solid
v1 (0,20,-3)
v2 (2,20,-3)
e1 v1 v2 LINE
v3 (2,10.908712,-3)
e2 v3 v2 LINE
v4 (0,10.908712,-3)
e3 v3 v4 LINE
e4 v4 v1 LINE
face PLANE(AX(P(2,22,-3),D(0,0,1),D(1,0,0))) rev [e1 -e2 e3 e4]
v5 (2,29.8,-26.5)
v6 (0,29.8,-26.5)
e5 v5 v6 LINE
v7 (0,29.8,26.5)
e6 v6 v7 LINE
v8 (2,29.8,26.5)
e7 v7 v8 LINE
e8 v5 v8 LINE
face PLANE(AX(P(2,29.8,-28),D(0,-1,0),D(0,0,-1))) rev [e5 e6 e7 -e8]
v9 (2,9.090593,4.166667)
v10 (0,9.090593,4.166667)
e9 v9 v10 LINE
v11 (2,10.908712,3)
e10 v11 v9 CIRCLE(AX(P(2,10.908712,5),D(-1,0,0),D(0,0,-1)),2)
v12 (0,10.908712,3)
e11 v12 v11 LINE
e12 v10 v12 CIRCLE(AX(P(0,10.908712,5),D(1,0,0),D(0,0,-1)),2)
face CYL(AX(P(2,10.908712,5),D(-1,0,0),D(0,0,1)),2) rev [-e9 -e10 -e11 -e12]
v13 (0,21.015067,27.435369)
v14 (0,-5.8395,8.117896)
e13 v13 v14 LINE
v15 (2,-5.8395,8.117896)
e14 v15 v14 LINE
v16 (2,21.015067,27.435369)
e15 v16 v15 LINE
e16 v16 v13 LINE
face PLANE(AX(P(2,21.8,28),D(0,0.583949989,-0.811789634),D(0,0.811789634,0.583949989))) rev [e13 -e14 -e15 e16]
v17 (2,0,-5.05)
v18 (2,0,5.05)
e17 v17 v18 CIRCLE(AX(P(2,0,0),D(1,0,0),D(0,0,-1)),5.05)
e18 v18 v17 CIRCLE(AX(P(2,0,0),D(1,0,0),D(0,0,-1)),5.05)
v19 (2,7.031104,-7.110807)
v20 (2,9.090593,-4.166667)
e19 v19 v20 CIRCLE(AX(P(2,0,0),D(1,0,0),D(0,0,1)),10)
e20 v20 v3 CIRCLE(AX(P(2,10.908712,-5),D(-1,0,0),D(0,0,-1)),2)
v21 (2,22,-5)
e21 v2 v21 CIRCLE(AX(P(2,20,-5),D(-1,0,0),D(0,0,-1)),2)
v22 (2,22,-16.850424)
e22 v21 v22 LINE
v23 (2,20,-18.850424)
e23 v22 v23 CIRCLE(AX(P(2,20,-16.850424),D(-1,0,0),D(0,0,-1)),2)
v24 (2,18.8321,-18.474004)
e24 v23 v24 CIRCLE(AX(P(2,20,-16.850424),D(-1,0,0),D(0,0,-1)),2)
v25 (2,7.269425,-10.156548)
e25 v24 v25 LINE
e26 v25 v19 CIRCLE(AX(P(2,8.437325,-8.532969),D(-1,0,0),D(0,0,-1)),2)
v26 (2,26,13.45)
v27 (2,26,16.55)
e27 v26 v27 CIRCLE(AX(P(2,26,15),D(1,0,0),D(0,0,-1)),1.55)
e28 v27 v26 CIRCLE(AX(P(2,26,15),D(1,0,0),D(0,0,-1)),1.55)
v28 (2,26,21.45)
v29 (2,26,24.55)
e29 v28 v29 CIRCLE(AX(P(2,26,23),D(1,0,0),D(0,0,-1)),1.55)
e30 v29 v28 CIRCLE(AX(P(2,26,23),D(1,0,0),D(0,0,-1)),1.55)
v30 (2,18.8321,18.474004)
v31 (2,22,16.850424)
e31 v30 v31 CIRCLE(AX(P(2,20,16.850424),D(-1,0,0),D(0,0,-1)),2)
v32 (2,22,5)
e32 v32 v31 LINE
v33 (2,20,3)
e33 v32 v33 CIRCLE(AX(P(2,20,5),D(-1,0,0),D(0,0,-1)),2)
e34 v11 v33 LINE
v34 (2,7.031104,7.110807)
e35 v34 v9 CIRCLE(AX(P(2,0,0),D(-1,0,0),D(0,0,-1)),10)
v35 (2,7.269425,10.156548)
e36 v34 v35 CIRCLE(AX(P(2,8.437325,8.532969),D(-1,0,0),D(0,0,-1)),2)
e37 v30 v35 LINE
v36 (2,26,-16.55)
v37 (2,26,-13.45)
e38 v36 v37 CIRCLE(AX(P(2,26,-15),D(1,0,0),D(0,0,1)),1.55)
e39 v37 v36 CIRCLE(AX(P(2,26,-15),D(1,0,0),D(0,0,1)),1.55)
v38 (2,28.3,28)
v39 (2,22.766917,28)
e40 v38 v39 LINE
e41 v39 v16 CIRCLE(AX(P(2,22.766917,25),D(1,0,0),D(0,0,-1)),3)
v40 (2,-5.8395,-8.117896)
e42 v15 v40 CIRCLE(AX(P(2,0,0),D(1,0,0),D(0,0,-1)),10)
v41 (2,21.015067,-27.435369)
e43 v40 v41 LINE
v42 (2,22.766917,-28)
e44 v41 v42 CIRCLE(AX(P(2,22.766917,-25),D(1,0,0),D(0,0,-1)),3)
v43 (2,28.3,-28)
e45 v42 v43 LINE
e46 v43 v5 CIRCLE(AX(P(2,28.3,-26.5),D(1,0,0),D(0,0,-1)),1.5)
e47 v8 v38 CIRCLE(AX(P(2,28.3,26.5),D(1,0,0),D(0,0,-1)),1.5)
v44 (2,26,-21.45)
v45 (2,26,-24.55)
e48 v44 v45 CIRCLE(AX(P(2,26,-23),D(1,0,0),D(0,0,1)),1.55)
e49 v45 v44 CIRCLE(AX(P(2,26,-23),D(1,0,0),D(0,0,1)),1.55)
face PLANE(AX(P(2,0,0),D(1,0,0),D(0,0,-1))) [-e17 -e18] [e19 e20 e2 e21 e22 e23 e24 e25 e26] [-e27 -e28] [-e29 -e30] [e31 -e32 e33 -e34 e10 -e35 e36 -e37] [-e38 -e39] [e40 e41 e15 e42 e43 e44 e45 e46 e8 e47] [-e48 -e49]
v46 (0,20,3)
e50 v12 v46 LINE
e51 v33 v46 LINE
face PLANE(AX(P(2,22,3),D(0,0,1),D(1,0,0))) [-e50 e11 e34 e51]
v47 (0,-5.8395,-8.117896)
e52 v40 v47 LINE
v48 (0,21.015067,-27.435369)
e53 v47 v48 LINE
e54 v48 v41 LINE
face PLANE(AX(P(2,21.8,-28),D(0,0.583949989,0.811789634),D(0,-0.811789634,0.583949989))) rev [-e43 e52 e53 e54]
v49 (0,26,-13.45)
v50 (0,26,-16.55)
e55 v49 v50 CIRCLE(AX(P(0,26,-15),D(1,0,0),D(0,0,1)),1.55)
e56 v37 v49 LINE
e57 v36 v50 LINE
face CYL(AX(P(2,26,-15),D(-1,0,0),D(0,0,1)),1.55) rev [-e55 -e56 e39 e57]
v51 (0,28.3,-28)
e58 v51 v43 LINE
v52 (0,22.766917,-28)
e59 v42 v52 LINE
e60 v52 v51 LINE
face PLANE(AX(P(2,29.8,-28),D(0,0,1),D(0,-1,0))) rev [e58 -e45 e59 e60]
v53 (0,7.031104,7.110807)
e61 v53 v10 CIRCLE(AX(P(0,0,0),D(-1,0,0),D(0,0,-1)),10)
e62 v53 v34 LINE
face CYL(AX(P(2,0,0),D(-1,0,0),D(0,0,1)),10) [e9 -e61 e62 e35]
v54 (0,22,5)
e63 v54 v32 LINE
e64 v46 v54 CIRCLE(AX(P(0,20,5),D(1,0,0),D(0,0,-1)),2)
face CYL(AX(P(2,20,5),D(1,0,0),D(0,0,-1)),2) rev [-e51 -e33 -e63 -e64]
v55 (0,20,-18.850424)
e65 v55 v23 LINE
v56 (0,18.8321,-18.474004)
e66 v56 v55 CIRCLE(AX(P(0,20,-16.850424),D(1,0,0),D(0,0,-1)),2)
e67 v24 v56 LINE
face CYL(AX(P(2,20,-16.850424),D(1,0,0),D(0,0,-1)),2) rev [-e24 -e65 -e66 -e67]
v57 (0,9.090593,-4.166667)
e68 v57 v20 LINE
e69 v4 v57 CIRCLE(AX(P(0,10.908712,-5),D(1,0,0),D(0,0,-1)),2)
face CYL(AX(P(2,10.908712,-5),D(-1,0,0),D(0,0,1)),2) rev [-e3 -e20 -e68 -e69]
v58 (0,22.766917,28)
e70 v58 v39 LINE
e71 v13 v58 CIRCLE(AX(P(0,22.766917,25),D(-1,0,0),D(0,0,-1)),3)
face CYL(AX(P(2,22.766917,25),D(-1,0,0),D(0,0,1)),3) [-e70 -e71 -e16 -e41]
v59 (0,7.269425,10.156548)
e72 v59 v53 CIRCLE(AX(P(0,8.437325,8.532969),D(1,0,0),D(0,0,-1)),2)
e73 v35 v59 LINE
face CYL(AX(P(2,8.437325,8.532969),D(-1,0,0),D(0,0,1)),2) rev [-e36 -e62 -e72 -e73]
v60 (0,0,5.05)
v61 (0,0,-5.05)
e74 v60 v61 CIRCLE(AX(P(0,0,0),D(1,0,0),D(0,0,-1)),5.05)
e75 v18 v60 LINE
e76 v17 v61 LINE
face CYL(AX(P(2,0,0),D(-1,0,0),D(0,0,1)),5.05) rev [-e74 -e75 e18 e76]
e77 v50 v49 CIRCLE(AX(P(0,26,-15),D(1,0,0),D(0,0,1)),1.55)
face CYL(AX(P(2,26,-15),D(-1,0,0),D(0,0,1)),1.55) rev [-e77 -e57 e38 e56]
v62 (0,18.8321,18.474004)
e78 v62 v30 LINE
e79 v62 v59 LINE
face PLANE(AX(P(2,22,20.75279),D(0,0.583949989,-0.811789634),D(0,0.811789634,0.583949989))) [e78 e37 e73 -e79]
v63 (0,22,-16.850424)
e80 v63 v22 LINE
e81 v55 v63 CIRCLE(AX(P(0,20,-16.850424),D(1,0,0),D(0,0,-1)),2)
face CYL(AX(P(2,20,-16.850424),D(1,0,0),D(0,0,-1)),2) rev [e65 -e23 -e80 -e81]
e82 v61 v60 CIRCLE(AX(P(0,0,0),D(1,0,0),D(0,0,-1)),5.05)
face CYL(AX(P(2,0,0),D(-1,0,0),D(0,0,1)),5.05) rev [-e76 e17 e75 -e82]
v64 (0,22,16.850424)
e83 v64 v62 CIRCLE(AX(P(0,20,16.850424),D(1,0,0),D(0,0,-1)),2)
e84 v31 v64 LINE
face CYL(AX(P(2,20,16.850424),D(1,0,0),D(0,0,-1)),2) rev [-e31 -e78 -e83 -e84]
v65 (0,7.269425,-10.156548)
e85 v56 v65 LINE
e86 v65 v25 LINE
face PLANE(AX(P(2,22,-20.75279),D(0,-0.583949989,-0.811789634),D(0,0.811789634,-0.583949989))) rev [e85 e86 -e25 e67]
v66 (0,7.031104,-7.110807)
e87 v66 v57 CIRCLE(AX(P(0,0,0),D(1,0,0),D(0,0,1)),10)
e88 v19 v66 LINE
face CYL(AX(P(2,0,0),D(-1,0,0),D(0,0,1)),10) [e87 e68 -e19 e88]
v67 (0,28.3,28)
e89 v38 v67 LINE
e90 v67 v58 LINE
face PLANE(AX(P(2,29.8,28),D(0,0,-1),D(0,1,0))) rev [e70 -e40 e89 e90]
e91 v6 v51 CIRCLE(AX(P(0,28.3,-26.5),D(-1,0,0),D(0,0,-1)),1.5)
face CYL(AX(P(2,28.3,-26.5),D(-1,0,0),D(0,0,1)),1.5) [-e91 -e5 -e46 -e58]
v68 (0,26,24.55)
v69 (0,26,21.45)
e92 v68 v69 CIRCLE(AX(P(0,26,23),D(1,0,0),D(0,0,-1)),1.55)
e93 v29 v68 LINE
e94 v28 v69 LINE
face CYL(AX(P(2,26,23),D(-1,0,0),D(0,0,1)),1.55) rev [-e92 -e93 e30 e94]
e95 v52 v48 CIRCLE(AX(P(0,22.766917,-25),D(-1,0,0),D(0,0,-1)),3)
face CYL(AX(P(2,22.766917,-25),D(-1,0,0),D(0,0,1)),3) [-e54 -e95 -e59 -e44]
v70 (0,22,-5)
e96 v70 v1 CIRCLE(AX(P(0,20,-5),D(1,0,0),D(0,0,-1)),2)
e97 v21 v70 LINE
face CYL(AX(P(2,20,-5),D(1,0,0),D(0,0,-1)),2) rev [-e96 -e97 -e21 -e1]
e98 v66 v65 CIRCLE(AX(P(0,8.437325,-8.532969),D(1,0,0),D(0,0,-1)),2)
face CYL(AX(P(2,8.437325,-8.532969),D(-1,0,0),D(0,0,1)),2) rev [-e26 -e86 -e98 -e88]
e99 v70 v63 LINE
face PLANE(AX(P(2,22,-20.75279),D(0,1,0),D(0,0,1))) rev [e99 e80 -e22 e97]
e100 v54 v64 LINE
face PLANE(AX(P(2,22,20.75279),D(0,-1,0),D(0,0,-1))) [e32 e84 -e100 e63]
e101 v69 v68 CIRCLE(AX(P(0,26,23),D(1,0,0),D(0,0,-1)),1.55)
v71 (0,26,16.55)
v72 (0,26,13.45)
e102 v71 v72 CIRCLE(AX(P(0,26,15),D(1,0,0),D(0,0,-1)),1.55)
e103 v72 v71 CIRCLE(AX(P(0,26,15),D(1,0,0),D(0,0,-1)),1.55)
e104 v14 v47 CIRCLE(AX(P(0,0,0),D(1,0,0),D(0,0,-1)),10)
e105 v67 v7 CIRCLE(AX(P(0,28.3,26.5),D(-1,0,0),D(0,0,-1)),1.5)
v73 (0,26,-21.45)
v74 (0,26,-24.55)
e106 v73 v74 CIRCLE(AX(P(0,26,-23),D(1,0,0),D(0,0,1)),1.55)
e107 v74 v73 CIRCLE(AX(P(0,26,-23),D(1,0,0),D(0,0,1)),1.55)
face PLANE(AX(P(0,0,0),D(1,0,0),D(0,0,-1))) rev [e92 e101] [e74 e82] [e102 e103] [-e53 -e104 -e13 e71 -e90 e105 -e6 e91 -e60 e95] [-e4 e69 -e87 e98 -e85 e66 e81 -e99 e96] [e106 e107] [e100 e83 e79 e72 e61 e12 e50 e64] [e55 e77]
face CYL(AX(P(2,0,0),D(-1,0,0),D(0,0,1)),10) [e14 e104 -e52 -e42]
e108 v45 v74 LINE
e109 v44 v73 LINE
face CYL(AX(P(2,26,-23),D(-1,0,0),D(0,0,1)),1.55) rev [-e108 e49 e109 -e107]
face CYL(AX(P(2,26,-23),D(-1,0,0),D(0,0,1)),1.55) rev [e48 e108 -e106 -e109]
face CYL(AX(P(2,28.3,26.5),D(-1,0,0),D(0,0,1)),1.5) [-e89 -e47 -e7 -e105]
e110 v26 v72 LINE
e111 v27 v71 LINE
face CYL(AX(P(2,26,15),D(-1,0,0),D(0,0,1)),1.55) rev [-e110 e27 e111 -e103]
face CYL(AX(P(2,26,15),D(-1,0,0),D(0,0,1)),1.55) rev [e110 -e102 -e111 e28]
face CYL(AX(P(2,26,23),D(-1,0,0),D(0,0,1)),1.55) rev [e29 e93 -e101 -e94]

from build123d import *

# Parameters (mm, degrees)
SKETCH_1_R          = 5.05
SKETCH_1_R_2        = 1.55
EXTRUDE_1_DEPTH     = 2
CUT_EXTRUDE_1_DEPTH = 41.93946751
FILLET_1_R          = 2
FILLET_2_R          = 2
FILLET_3_R          = 3
FILLET_4_R          = 1.5


with BuildPart() as part:
    # 草图1 → 凸台-拉伸1 (new body)
    with BuildSketch(Plane(origin=(0, 0, 0), x_dir=(0, 0, -1), z_dir=(1, 0, 0))):
        with BuildLine():
            Line((-28, 29.8), (-28, 21.8))
            Line((-28, 21.8), (-8.117896343, -5.83949989))
            ThreePointArc((-8.117896343, -5.83949989), (0, -10), (8.117896343, -5.83949989))
            Line((8.117896343, -5.83949989), (28, 21.8))
            Line((28, 21.8), (28, 29.8))
            Line((28, 29.8), (-28, 29.8))
        make_face()
        Circle(SKETCH_1_R, mode=Mode.SUBTRACT)
        with Locations((-15, 26)):
            Circle(SKETCH_1_R_2, mode=Mode.SUBTRACT)
        with Locations((-23, 26)):
            Circle(SKETCH_1_R_2, mode=Mode.SUBTRACT)
        with Locations(Location((23, 26, 0), (0, 0, 180))):
            Circle(SKETCH_1_R_2, mode=Mode.SUBTRACT)
        with Locations(Location((15, 26, 0), (0, 0, 180))):
            Circle(SKETCH_1_R_2, mode=Mode.SUBTRACT)
    extrude(amount=EXTRUDE_1_DEPTH)

    # 草图2 → 切除-拉伸1 (cut, through all)
    with BuildSketch(Plane(origin=(0, 0, 0), x_dir=(0, 0, -1), z_dir=(1, 0, 0))):
        with BuildLine():
            Line((-3, 22), (-3, 9.539392014))
            ThreePointArc((-3, 9.539392014), (-6.209058392, 7.838851566), (-8.599148591, 5.104374939))
            Line((-8.599148591, 5.104374939), (-20.752789943, 22))
            Line((-20.752789943, 22), (-3, 22))
        make_face()
    cut_extrude_1 = extrude(amount=CUT_EXTRUDE_1_DEPTH, mode=Mode.SUBTRACT)

    # 圆角1
    fillet_1_edges = [part.edges().sort_by_distance(p)[0] for p in [
        (1, 22, 3),
        (1, 22, 20.752789943),
        (1, 5.104374939, 8.599148591),
        (1, 9.539392014, 3),
    ]]
    fillet(fillet_1_edges, radius=FILLET_1_R)

    # 镜向1: 切除-拉伸1 across plane
    add(cut_extrude_1.mirror(Plane.XY), mode=Mode.SUBTRACT)

    # 圆角2
    fillet_2_edges = [part.edges().sort_by_distance(p)[0] for p in [
        (1, 22, -20.752789943),
        (1, 22, -3),
        (1, 9.539392014, -3),
        (1, 5.104374939, -8.599148591),
    ]]
    fillet(fillet_2_edges, radius=FILLET_2_R)

    # 圆角3
    fillet_3_edges = [part.edges().sort_by_distance(p)[0] for p in [
        (1, 21.8, -28),
        (1, 21.8, 28),
    ]]
    fillet(fillet_3_edges, radius=FILLET_3_R)

    # 圆角4
    fillet_4_edges = [part.edges().sort_by_distance(p)[0] for p in [
        (1, 29.8, -28),
        (1, 29.8, 28),
    ]]
    fillet(fillet_4_edges, radius=FILLET_4_R)


solid = part.part
